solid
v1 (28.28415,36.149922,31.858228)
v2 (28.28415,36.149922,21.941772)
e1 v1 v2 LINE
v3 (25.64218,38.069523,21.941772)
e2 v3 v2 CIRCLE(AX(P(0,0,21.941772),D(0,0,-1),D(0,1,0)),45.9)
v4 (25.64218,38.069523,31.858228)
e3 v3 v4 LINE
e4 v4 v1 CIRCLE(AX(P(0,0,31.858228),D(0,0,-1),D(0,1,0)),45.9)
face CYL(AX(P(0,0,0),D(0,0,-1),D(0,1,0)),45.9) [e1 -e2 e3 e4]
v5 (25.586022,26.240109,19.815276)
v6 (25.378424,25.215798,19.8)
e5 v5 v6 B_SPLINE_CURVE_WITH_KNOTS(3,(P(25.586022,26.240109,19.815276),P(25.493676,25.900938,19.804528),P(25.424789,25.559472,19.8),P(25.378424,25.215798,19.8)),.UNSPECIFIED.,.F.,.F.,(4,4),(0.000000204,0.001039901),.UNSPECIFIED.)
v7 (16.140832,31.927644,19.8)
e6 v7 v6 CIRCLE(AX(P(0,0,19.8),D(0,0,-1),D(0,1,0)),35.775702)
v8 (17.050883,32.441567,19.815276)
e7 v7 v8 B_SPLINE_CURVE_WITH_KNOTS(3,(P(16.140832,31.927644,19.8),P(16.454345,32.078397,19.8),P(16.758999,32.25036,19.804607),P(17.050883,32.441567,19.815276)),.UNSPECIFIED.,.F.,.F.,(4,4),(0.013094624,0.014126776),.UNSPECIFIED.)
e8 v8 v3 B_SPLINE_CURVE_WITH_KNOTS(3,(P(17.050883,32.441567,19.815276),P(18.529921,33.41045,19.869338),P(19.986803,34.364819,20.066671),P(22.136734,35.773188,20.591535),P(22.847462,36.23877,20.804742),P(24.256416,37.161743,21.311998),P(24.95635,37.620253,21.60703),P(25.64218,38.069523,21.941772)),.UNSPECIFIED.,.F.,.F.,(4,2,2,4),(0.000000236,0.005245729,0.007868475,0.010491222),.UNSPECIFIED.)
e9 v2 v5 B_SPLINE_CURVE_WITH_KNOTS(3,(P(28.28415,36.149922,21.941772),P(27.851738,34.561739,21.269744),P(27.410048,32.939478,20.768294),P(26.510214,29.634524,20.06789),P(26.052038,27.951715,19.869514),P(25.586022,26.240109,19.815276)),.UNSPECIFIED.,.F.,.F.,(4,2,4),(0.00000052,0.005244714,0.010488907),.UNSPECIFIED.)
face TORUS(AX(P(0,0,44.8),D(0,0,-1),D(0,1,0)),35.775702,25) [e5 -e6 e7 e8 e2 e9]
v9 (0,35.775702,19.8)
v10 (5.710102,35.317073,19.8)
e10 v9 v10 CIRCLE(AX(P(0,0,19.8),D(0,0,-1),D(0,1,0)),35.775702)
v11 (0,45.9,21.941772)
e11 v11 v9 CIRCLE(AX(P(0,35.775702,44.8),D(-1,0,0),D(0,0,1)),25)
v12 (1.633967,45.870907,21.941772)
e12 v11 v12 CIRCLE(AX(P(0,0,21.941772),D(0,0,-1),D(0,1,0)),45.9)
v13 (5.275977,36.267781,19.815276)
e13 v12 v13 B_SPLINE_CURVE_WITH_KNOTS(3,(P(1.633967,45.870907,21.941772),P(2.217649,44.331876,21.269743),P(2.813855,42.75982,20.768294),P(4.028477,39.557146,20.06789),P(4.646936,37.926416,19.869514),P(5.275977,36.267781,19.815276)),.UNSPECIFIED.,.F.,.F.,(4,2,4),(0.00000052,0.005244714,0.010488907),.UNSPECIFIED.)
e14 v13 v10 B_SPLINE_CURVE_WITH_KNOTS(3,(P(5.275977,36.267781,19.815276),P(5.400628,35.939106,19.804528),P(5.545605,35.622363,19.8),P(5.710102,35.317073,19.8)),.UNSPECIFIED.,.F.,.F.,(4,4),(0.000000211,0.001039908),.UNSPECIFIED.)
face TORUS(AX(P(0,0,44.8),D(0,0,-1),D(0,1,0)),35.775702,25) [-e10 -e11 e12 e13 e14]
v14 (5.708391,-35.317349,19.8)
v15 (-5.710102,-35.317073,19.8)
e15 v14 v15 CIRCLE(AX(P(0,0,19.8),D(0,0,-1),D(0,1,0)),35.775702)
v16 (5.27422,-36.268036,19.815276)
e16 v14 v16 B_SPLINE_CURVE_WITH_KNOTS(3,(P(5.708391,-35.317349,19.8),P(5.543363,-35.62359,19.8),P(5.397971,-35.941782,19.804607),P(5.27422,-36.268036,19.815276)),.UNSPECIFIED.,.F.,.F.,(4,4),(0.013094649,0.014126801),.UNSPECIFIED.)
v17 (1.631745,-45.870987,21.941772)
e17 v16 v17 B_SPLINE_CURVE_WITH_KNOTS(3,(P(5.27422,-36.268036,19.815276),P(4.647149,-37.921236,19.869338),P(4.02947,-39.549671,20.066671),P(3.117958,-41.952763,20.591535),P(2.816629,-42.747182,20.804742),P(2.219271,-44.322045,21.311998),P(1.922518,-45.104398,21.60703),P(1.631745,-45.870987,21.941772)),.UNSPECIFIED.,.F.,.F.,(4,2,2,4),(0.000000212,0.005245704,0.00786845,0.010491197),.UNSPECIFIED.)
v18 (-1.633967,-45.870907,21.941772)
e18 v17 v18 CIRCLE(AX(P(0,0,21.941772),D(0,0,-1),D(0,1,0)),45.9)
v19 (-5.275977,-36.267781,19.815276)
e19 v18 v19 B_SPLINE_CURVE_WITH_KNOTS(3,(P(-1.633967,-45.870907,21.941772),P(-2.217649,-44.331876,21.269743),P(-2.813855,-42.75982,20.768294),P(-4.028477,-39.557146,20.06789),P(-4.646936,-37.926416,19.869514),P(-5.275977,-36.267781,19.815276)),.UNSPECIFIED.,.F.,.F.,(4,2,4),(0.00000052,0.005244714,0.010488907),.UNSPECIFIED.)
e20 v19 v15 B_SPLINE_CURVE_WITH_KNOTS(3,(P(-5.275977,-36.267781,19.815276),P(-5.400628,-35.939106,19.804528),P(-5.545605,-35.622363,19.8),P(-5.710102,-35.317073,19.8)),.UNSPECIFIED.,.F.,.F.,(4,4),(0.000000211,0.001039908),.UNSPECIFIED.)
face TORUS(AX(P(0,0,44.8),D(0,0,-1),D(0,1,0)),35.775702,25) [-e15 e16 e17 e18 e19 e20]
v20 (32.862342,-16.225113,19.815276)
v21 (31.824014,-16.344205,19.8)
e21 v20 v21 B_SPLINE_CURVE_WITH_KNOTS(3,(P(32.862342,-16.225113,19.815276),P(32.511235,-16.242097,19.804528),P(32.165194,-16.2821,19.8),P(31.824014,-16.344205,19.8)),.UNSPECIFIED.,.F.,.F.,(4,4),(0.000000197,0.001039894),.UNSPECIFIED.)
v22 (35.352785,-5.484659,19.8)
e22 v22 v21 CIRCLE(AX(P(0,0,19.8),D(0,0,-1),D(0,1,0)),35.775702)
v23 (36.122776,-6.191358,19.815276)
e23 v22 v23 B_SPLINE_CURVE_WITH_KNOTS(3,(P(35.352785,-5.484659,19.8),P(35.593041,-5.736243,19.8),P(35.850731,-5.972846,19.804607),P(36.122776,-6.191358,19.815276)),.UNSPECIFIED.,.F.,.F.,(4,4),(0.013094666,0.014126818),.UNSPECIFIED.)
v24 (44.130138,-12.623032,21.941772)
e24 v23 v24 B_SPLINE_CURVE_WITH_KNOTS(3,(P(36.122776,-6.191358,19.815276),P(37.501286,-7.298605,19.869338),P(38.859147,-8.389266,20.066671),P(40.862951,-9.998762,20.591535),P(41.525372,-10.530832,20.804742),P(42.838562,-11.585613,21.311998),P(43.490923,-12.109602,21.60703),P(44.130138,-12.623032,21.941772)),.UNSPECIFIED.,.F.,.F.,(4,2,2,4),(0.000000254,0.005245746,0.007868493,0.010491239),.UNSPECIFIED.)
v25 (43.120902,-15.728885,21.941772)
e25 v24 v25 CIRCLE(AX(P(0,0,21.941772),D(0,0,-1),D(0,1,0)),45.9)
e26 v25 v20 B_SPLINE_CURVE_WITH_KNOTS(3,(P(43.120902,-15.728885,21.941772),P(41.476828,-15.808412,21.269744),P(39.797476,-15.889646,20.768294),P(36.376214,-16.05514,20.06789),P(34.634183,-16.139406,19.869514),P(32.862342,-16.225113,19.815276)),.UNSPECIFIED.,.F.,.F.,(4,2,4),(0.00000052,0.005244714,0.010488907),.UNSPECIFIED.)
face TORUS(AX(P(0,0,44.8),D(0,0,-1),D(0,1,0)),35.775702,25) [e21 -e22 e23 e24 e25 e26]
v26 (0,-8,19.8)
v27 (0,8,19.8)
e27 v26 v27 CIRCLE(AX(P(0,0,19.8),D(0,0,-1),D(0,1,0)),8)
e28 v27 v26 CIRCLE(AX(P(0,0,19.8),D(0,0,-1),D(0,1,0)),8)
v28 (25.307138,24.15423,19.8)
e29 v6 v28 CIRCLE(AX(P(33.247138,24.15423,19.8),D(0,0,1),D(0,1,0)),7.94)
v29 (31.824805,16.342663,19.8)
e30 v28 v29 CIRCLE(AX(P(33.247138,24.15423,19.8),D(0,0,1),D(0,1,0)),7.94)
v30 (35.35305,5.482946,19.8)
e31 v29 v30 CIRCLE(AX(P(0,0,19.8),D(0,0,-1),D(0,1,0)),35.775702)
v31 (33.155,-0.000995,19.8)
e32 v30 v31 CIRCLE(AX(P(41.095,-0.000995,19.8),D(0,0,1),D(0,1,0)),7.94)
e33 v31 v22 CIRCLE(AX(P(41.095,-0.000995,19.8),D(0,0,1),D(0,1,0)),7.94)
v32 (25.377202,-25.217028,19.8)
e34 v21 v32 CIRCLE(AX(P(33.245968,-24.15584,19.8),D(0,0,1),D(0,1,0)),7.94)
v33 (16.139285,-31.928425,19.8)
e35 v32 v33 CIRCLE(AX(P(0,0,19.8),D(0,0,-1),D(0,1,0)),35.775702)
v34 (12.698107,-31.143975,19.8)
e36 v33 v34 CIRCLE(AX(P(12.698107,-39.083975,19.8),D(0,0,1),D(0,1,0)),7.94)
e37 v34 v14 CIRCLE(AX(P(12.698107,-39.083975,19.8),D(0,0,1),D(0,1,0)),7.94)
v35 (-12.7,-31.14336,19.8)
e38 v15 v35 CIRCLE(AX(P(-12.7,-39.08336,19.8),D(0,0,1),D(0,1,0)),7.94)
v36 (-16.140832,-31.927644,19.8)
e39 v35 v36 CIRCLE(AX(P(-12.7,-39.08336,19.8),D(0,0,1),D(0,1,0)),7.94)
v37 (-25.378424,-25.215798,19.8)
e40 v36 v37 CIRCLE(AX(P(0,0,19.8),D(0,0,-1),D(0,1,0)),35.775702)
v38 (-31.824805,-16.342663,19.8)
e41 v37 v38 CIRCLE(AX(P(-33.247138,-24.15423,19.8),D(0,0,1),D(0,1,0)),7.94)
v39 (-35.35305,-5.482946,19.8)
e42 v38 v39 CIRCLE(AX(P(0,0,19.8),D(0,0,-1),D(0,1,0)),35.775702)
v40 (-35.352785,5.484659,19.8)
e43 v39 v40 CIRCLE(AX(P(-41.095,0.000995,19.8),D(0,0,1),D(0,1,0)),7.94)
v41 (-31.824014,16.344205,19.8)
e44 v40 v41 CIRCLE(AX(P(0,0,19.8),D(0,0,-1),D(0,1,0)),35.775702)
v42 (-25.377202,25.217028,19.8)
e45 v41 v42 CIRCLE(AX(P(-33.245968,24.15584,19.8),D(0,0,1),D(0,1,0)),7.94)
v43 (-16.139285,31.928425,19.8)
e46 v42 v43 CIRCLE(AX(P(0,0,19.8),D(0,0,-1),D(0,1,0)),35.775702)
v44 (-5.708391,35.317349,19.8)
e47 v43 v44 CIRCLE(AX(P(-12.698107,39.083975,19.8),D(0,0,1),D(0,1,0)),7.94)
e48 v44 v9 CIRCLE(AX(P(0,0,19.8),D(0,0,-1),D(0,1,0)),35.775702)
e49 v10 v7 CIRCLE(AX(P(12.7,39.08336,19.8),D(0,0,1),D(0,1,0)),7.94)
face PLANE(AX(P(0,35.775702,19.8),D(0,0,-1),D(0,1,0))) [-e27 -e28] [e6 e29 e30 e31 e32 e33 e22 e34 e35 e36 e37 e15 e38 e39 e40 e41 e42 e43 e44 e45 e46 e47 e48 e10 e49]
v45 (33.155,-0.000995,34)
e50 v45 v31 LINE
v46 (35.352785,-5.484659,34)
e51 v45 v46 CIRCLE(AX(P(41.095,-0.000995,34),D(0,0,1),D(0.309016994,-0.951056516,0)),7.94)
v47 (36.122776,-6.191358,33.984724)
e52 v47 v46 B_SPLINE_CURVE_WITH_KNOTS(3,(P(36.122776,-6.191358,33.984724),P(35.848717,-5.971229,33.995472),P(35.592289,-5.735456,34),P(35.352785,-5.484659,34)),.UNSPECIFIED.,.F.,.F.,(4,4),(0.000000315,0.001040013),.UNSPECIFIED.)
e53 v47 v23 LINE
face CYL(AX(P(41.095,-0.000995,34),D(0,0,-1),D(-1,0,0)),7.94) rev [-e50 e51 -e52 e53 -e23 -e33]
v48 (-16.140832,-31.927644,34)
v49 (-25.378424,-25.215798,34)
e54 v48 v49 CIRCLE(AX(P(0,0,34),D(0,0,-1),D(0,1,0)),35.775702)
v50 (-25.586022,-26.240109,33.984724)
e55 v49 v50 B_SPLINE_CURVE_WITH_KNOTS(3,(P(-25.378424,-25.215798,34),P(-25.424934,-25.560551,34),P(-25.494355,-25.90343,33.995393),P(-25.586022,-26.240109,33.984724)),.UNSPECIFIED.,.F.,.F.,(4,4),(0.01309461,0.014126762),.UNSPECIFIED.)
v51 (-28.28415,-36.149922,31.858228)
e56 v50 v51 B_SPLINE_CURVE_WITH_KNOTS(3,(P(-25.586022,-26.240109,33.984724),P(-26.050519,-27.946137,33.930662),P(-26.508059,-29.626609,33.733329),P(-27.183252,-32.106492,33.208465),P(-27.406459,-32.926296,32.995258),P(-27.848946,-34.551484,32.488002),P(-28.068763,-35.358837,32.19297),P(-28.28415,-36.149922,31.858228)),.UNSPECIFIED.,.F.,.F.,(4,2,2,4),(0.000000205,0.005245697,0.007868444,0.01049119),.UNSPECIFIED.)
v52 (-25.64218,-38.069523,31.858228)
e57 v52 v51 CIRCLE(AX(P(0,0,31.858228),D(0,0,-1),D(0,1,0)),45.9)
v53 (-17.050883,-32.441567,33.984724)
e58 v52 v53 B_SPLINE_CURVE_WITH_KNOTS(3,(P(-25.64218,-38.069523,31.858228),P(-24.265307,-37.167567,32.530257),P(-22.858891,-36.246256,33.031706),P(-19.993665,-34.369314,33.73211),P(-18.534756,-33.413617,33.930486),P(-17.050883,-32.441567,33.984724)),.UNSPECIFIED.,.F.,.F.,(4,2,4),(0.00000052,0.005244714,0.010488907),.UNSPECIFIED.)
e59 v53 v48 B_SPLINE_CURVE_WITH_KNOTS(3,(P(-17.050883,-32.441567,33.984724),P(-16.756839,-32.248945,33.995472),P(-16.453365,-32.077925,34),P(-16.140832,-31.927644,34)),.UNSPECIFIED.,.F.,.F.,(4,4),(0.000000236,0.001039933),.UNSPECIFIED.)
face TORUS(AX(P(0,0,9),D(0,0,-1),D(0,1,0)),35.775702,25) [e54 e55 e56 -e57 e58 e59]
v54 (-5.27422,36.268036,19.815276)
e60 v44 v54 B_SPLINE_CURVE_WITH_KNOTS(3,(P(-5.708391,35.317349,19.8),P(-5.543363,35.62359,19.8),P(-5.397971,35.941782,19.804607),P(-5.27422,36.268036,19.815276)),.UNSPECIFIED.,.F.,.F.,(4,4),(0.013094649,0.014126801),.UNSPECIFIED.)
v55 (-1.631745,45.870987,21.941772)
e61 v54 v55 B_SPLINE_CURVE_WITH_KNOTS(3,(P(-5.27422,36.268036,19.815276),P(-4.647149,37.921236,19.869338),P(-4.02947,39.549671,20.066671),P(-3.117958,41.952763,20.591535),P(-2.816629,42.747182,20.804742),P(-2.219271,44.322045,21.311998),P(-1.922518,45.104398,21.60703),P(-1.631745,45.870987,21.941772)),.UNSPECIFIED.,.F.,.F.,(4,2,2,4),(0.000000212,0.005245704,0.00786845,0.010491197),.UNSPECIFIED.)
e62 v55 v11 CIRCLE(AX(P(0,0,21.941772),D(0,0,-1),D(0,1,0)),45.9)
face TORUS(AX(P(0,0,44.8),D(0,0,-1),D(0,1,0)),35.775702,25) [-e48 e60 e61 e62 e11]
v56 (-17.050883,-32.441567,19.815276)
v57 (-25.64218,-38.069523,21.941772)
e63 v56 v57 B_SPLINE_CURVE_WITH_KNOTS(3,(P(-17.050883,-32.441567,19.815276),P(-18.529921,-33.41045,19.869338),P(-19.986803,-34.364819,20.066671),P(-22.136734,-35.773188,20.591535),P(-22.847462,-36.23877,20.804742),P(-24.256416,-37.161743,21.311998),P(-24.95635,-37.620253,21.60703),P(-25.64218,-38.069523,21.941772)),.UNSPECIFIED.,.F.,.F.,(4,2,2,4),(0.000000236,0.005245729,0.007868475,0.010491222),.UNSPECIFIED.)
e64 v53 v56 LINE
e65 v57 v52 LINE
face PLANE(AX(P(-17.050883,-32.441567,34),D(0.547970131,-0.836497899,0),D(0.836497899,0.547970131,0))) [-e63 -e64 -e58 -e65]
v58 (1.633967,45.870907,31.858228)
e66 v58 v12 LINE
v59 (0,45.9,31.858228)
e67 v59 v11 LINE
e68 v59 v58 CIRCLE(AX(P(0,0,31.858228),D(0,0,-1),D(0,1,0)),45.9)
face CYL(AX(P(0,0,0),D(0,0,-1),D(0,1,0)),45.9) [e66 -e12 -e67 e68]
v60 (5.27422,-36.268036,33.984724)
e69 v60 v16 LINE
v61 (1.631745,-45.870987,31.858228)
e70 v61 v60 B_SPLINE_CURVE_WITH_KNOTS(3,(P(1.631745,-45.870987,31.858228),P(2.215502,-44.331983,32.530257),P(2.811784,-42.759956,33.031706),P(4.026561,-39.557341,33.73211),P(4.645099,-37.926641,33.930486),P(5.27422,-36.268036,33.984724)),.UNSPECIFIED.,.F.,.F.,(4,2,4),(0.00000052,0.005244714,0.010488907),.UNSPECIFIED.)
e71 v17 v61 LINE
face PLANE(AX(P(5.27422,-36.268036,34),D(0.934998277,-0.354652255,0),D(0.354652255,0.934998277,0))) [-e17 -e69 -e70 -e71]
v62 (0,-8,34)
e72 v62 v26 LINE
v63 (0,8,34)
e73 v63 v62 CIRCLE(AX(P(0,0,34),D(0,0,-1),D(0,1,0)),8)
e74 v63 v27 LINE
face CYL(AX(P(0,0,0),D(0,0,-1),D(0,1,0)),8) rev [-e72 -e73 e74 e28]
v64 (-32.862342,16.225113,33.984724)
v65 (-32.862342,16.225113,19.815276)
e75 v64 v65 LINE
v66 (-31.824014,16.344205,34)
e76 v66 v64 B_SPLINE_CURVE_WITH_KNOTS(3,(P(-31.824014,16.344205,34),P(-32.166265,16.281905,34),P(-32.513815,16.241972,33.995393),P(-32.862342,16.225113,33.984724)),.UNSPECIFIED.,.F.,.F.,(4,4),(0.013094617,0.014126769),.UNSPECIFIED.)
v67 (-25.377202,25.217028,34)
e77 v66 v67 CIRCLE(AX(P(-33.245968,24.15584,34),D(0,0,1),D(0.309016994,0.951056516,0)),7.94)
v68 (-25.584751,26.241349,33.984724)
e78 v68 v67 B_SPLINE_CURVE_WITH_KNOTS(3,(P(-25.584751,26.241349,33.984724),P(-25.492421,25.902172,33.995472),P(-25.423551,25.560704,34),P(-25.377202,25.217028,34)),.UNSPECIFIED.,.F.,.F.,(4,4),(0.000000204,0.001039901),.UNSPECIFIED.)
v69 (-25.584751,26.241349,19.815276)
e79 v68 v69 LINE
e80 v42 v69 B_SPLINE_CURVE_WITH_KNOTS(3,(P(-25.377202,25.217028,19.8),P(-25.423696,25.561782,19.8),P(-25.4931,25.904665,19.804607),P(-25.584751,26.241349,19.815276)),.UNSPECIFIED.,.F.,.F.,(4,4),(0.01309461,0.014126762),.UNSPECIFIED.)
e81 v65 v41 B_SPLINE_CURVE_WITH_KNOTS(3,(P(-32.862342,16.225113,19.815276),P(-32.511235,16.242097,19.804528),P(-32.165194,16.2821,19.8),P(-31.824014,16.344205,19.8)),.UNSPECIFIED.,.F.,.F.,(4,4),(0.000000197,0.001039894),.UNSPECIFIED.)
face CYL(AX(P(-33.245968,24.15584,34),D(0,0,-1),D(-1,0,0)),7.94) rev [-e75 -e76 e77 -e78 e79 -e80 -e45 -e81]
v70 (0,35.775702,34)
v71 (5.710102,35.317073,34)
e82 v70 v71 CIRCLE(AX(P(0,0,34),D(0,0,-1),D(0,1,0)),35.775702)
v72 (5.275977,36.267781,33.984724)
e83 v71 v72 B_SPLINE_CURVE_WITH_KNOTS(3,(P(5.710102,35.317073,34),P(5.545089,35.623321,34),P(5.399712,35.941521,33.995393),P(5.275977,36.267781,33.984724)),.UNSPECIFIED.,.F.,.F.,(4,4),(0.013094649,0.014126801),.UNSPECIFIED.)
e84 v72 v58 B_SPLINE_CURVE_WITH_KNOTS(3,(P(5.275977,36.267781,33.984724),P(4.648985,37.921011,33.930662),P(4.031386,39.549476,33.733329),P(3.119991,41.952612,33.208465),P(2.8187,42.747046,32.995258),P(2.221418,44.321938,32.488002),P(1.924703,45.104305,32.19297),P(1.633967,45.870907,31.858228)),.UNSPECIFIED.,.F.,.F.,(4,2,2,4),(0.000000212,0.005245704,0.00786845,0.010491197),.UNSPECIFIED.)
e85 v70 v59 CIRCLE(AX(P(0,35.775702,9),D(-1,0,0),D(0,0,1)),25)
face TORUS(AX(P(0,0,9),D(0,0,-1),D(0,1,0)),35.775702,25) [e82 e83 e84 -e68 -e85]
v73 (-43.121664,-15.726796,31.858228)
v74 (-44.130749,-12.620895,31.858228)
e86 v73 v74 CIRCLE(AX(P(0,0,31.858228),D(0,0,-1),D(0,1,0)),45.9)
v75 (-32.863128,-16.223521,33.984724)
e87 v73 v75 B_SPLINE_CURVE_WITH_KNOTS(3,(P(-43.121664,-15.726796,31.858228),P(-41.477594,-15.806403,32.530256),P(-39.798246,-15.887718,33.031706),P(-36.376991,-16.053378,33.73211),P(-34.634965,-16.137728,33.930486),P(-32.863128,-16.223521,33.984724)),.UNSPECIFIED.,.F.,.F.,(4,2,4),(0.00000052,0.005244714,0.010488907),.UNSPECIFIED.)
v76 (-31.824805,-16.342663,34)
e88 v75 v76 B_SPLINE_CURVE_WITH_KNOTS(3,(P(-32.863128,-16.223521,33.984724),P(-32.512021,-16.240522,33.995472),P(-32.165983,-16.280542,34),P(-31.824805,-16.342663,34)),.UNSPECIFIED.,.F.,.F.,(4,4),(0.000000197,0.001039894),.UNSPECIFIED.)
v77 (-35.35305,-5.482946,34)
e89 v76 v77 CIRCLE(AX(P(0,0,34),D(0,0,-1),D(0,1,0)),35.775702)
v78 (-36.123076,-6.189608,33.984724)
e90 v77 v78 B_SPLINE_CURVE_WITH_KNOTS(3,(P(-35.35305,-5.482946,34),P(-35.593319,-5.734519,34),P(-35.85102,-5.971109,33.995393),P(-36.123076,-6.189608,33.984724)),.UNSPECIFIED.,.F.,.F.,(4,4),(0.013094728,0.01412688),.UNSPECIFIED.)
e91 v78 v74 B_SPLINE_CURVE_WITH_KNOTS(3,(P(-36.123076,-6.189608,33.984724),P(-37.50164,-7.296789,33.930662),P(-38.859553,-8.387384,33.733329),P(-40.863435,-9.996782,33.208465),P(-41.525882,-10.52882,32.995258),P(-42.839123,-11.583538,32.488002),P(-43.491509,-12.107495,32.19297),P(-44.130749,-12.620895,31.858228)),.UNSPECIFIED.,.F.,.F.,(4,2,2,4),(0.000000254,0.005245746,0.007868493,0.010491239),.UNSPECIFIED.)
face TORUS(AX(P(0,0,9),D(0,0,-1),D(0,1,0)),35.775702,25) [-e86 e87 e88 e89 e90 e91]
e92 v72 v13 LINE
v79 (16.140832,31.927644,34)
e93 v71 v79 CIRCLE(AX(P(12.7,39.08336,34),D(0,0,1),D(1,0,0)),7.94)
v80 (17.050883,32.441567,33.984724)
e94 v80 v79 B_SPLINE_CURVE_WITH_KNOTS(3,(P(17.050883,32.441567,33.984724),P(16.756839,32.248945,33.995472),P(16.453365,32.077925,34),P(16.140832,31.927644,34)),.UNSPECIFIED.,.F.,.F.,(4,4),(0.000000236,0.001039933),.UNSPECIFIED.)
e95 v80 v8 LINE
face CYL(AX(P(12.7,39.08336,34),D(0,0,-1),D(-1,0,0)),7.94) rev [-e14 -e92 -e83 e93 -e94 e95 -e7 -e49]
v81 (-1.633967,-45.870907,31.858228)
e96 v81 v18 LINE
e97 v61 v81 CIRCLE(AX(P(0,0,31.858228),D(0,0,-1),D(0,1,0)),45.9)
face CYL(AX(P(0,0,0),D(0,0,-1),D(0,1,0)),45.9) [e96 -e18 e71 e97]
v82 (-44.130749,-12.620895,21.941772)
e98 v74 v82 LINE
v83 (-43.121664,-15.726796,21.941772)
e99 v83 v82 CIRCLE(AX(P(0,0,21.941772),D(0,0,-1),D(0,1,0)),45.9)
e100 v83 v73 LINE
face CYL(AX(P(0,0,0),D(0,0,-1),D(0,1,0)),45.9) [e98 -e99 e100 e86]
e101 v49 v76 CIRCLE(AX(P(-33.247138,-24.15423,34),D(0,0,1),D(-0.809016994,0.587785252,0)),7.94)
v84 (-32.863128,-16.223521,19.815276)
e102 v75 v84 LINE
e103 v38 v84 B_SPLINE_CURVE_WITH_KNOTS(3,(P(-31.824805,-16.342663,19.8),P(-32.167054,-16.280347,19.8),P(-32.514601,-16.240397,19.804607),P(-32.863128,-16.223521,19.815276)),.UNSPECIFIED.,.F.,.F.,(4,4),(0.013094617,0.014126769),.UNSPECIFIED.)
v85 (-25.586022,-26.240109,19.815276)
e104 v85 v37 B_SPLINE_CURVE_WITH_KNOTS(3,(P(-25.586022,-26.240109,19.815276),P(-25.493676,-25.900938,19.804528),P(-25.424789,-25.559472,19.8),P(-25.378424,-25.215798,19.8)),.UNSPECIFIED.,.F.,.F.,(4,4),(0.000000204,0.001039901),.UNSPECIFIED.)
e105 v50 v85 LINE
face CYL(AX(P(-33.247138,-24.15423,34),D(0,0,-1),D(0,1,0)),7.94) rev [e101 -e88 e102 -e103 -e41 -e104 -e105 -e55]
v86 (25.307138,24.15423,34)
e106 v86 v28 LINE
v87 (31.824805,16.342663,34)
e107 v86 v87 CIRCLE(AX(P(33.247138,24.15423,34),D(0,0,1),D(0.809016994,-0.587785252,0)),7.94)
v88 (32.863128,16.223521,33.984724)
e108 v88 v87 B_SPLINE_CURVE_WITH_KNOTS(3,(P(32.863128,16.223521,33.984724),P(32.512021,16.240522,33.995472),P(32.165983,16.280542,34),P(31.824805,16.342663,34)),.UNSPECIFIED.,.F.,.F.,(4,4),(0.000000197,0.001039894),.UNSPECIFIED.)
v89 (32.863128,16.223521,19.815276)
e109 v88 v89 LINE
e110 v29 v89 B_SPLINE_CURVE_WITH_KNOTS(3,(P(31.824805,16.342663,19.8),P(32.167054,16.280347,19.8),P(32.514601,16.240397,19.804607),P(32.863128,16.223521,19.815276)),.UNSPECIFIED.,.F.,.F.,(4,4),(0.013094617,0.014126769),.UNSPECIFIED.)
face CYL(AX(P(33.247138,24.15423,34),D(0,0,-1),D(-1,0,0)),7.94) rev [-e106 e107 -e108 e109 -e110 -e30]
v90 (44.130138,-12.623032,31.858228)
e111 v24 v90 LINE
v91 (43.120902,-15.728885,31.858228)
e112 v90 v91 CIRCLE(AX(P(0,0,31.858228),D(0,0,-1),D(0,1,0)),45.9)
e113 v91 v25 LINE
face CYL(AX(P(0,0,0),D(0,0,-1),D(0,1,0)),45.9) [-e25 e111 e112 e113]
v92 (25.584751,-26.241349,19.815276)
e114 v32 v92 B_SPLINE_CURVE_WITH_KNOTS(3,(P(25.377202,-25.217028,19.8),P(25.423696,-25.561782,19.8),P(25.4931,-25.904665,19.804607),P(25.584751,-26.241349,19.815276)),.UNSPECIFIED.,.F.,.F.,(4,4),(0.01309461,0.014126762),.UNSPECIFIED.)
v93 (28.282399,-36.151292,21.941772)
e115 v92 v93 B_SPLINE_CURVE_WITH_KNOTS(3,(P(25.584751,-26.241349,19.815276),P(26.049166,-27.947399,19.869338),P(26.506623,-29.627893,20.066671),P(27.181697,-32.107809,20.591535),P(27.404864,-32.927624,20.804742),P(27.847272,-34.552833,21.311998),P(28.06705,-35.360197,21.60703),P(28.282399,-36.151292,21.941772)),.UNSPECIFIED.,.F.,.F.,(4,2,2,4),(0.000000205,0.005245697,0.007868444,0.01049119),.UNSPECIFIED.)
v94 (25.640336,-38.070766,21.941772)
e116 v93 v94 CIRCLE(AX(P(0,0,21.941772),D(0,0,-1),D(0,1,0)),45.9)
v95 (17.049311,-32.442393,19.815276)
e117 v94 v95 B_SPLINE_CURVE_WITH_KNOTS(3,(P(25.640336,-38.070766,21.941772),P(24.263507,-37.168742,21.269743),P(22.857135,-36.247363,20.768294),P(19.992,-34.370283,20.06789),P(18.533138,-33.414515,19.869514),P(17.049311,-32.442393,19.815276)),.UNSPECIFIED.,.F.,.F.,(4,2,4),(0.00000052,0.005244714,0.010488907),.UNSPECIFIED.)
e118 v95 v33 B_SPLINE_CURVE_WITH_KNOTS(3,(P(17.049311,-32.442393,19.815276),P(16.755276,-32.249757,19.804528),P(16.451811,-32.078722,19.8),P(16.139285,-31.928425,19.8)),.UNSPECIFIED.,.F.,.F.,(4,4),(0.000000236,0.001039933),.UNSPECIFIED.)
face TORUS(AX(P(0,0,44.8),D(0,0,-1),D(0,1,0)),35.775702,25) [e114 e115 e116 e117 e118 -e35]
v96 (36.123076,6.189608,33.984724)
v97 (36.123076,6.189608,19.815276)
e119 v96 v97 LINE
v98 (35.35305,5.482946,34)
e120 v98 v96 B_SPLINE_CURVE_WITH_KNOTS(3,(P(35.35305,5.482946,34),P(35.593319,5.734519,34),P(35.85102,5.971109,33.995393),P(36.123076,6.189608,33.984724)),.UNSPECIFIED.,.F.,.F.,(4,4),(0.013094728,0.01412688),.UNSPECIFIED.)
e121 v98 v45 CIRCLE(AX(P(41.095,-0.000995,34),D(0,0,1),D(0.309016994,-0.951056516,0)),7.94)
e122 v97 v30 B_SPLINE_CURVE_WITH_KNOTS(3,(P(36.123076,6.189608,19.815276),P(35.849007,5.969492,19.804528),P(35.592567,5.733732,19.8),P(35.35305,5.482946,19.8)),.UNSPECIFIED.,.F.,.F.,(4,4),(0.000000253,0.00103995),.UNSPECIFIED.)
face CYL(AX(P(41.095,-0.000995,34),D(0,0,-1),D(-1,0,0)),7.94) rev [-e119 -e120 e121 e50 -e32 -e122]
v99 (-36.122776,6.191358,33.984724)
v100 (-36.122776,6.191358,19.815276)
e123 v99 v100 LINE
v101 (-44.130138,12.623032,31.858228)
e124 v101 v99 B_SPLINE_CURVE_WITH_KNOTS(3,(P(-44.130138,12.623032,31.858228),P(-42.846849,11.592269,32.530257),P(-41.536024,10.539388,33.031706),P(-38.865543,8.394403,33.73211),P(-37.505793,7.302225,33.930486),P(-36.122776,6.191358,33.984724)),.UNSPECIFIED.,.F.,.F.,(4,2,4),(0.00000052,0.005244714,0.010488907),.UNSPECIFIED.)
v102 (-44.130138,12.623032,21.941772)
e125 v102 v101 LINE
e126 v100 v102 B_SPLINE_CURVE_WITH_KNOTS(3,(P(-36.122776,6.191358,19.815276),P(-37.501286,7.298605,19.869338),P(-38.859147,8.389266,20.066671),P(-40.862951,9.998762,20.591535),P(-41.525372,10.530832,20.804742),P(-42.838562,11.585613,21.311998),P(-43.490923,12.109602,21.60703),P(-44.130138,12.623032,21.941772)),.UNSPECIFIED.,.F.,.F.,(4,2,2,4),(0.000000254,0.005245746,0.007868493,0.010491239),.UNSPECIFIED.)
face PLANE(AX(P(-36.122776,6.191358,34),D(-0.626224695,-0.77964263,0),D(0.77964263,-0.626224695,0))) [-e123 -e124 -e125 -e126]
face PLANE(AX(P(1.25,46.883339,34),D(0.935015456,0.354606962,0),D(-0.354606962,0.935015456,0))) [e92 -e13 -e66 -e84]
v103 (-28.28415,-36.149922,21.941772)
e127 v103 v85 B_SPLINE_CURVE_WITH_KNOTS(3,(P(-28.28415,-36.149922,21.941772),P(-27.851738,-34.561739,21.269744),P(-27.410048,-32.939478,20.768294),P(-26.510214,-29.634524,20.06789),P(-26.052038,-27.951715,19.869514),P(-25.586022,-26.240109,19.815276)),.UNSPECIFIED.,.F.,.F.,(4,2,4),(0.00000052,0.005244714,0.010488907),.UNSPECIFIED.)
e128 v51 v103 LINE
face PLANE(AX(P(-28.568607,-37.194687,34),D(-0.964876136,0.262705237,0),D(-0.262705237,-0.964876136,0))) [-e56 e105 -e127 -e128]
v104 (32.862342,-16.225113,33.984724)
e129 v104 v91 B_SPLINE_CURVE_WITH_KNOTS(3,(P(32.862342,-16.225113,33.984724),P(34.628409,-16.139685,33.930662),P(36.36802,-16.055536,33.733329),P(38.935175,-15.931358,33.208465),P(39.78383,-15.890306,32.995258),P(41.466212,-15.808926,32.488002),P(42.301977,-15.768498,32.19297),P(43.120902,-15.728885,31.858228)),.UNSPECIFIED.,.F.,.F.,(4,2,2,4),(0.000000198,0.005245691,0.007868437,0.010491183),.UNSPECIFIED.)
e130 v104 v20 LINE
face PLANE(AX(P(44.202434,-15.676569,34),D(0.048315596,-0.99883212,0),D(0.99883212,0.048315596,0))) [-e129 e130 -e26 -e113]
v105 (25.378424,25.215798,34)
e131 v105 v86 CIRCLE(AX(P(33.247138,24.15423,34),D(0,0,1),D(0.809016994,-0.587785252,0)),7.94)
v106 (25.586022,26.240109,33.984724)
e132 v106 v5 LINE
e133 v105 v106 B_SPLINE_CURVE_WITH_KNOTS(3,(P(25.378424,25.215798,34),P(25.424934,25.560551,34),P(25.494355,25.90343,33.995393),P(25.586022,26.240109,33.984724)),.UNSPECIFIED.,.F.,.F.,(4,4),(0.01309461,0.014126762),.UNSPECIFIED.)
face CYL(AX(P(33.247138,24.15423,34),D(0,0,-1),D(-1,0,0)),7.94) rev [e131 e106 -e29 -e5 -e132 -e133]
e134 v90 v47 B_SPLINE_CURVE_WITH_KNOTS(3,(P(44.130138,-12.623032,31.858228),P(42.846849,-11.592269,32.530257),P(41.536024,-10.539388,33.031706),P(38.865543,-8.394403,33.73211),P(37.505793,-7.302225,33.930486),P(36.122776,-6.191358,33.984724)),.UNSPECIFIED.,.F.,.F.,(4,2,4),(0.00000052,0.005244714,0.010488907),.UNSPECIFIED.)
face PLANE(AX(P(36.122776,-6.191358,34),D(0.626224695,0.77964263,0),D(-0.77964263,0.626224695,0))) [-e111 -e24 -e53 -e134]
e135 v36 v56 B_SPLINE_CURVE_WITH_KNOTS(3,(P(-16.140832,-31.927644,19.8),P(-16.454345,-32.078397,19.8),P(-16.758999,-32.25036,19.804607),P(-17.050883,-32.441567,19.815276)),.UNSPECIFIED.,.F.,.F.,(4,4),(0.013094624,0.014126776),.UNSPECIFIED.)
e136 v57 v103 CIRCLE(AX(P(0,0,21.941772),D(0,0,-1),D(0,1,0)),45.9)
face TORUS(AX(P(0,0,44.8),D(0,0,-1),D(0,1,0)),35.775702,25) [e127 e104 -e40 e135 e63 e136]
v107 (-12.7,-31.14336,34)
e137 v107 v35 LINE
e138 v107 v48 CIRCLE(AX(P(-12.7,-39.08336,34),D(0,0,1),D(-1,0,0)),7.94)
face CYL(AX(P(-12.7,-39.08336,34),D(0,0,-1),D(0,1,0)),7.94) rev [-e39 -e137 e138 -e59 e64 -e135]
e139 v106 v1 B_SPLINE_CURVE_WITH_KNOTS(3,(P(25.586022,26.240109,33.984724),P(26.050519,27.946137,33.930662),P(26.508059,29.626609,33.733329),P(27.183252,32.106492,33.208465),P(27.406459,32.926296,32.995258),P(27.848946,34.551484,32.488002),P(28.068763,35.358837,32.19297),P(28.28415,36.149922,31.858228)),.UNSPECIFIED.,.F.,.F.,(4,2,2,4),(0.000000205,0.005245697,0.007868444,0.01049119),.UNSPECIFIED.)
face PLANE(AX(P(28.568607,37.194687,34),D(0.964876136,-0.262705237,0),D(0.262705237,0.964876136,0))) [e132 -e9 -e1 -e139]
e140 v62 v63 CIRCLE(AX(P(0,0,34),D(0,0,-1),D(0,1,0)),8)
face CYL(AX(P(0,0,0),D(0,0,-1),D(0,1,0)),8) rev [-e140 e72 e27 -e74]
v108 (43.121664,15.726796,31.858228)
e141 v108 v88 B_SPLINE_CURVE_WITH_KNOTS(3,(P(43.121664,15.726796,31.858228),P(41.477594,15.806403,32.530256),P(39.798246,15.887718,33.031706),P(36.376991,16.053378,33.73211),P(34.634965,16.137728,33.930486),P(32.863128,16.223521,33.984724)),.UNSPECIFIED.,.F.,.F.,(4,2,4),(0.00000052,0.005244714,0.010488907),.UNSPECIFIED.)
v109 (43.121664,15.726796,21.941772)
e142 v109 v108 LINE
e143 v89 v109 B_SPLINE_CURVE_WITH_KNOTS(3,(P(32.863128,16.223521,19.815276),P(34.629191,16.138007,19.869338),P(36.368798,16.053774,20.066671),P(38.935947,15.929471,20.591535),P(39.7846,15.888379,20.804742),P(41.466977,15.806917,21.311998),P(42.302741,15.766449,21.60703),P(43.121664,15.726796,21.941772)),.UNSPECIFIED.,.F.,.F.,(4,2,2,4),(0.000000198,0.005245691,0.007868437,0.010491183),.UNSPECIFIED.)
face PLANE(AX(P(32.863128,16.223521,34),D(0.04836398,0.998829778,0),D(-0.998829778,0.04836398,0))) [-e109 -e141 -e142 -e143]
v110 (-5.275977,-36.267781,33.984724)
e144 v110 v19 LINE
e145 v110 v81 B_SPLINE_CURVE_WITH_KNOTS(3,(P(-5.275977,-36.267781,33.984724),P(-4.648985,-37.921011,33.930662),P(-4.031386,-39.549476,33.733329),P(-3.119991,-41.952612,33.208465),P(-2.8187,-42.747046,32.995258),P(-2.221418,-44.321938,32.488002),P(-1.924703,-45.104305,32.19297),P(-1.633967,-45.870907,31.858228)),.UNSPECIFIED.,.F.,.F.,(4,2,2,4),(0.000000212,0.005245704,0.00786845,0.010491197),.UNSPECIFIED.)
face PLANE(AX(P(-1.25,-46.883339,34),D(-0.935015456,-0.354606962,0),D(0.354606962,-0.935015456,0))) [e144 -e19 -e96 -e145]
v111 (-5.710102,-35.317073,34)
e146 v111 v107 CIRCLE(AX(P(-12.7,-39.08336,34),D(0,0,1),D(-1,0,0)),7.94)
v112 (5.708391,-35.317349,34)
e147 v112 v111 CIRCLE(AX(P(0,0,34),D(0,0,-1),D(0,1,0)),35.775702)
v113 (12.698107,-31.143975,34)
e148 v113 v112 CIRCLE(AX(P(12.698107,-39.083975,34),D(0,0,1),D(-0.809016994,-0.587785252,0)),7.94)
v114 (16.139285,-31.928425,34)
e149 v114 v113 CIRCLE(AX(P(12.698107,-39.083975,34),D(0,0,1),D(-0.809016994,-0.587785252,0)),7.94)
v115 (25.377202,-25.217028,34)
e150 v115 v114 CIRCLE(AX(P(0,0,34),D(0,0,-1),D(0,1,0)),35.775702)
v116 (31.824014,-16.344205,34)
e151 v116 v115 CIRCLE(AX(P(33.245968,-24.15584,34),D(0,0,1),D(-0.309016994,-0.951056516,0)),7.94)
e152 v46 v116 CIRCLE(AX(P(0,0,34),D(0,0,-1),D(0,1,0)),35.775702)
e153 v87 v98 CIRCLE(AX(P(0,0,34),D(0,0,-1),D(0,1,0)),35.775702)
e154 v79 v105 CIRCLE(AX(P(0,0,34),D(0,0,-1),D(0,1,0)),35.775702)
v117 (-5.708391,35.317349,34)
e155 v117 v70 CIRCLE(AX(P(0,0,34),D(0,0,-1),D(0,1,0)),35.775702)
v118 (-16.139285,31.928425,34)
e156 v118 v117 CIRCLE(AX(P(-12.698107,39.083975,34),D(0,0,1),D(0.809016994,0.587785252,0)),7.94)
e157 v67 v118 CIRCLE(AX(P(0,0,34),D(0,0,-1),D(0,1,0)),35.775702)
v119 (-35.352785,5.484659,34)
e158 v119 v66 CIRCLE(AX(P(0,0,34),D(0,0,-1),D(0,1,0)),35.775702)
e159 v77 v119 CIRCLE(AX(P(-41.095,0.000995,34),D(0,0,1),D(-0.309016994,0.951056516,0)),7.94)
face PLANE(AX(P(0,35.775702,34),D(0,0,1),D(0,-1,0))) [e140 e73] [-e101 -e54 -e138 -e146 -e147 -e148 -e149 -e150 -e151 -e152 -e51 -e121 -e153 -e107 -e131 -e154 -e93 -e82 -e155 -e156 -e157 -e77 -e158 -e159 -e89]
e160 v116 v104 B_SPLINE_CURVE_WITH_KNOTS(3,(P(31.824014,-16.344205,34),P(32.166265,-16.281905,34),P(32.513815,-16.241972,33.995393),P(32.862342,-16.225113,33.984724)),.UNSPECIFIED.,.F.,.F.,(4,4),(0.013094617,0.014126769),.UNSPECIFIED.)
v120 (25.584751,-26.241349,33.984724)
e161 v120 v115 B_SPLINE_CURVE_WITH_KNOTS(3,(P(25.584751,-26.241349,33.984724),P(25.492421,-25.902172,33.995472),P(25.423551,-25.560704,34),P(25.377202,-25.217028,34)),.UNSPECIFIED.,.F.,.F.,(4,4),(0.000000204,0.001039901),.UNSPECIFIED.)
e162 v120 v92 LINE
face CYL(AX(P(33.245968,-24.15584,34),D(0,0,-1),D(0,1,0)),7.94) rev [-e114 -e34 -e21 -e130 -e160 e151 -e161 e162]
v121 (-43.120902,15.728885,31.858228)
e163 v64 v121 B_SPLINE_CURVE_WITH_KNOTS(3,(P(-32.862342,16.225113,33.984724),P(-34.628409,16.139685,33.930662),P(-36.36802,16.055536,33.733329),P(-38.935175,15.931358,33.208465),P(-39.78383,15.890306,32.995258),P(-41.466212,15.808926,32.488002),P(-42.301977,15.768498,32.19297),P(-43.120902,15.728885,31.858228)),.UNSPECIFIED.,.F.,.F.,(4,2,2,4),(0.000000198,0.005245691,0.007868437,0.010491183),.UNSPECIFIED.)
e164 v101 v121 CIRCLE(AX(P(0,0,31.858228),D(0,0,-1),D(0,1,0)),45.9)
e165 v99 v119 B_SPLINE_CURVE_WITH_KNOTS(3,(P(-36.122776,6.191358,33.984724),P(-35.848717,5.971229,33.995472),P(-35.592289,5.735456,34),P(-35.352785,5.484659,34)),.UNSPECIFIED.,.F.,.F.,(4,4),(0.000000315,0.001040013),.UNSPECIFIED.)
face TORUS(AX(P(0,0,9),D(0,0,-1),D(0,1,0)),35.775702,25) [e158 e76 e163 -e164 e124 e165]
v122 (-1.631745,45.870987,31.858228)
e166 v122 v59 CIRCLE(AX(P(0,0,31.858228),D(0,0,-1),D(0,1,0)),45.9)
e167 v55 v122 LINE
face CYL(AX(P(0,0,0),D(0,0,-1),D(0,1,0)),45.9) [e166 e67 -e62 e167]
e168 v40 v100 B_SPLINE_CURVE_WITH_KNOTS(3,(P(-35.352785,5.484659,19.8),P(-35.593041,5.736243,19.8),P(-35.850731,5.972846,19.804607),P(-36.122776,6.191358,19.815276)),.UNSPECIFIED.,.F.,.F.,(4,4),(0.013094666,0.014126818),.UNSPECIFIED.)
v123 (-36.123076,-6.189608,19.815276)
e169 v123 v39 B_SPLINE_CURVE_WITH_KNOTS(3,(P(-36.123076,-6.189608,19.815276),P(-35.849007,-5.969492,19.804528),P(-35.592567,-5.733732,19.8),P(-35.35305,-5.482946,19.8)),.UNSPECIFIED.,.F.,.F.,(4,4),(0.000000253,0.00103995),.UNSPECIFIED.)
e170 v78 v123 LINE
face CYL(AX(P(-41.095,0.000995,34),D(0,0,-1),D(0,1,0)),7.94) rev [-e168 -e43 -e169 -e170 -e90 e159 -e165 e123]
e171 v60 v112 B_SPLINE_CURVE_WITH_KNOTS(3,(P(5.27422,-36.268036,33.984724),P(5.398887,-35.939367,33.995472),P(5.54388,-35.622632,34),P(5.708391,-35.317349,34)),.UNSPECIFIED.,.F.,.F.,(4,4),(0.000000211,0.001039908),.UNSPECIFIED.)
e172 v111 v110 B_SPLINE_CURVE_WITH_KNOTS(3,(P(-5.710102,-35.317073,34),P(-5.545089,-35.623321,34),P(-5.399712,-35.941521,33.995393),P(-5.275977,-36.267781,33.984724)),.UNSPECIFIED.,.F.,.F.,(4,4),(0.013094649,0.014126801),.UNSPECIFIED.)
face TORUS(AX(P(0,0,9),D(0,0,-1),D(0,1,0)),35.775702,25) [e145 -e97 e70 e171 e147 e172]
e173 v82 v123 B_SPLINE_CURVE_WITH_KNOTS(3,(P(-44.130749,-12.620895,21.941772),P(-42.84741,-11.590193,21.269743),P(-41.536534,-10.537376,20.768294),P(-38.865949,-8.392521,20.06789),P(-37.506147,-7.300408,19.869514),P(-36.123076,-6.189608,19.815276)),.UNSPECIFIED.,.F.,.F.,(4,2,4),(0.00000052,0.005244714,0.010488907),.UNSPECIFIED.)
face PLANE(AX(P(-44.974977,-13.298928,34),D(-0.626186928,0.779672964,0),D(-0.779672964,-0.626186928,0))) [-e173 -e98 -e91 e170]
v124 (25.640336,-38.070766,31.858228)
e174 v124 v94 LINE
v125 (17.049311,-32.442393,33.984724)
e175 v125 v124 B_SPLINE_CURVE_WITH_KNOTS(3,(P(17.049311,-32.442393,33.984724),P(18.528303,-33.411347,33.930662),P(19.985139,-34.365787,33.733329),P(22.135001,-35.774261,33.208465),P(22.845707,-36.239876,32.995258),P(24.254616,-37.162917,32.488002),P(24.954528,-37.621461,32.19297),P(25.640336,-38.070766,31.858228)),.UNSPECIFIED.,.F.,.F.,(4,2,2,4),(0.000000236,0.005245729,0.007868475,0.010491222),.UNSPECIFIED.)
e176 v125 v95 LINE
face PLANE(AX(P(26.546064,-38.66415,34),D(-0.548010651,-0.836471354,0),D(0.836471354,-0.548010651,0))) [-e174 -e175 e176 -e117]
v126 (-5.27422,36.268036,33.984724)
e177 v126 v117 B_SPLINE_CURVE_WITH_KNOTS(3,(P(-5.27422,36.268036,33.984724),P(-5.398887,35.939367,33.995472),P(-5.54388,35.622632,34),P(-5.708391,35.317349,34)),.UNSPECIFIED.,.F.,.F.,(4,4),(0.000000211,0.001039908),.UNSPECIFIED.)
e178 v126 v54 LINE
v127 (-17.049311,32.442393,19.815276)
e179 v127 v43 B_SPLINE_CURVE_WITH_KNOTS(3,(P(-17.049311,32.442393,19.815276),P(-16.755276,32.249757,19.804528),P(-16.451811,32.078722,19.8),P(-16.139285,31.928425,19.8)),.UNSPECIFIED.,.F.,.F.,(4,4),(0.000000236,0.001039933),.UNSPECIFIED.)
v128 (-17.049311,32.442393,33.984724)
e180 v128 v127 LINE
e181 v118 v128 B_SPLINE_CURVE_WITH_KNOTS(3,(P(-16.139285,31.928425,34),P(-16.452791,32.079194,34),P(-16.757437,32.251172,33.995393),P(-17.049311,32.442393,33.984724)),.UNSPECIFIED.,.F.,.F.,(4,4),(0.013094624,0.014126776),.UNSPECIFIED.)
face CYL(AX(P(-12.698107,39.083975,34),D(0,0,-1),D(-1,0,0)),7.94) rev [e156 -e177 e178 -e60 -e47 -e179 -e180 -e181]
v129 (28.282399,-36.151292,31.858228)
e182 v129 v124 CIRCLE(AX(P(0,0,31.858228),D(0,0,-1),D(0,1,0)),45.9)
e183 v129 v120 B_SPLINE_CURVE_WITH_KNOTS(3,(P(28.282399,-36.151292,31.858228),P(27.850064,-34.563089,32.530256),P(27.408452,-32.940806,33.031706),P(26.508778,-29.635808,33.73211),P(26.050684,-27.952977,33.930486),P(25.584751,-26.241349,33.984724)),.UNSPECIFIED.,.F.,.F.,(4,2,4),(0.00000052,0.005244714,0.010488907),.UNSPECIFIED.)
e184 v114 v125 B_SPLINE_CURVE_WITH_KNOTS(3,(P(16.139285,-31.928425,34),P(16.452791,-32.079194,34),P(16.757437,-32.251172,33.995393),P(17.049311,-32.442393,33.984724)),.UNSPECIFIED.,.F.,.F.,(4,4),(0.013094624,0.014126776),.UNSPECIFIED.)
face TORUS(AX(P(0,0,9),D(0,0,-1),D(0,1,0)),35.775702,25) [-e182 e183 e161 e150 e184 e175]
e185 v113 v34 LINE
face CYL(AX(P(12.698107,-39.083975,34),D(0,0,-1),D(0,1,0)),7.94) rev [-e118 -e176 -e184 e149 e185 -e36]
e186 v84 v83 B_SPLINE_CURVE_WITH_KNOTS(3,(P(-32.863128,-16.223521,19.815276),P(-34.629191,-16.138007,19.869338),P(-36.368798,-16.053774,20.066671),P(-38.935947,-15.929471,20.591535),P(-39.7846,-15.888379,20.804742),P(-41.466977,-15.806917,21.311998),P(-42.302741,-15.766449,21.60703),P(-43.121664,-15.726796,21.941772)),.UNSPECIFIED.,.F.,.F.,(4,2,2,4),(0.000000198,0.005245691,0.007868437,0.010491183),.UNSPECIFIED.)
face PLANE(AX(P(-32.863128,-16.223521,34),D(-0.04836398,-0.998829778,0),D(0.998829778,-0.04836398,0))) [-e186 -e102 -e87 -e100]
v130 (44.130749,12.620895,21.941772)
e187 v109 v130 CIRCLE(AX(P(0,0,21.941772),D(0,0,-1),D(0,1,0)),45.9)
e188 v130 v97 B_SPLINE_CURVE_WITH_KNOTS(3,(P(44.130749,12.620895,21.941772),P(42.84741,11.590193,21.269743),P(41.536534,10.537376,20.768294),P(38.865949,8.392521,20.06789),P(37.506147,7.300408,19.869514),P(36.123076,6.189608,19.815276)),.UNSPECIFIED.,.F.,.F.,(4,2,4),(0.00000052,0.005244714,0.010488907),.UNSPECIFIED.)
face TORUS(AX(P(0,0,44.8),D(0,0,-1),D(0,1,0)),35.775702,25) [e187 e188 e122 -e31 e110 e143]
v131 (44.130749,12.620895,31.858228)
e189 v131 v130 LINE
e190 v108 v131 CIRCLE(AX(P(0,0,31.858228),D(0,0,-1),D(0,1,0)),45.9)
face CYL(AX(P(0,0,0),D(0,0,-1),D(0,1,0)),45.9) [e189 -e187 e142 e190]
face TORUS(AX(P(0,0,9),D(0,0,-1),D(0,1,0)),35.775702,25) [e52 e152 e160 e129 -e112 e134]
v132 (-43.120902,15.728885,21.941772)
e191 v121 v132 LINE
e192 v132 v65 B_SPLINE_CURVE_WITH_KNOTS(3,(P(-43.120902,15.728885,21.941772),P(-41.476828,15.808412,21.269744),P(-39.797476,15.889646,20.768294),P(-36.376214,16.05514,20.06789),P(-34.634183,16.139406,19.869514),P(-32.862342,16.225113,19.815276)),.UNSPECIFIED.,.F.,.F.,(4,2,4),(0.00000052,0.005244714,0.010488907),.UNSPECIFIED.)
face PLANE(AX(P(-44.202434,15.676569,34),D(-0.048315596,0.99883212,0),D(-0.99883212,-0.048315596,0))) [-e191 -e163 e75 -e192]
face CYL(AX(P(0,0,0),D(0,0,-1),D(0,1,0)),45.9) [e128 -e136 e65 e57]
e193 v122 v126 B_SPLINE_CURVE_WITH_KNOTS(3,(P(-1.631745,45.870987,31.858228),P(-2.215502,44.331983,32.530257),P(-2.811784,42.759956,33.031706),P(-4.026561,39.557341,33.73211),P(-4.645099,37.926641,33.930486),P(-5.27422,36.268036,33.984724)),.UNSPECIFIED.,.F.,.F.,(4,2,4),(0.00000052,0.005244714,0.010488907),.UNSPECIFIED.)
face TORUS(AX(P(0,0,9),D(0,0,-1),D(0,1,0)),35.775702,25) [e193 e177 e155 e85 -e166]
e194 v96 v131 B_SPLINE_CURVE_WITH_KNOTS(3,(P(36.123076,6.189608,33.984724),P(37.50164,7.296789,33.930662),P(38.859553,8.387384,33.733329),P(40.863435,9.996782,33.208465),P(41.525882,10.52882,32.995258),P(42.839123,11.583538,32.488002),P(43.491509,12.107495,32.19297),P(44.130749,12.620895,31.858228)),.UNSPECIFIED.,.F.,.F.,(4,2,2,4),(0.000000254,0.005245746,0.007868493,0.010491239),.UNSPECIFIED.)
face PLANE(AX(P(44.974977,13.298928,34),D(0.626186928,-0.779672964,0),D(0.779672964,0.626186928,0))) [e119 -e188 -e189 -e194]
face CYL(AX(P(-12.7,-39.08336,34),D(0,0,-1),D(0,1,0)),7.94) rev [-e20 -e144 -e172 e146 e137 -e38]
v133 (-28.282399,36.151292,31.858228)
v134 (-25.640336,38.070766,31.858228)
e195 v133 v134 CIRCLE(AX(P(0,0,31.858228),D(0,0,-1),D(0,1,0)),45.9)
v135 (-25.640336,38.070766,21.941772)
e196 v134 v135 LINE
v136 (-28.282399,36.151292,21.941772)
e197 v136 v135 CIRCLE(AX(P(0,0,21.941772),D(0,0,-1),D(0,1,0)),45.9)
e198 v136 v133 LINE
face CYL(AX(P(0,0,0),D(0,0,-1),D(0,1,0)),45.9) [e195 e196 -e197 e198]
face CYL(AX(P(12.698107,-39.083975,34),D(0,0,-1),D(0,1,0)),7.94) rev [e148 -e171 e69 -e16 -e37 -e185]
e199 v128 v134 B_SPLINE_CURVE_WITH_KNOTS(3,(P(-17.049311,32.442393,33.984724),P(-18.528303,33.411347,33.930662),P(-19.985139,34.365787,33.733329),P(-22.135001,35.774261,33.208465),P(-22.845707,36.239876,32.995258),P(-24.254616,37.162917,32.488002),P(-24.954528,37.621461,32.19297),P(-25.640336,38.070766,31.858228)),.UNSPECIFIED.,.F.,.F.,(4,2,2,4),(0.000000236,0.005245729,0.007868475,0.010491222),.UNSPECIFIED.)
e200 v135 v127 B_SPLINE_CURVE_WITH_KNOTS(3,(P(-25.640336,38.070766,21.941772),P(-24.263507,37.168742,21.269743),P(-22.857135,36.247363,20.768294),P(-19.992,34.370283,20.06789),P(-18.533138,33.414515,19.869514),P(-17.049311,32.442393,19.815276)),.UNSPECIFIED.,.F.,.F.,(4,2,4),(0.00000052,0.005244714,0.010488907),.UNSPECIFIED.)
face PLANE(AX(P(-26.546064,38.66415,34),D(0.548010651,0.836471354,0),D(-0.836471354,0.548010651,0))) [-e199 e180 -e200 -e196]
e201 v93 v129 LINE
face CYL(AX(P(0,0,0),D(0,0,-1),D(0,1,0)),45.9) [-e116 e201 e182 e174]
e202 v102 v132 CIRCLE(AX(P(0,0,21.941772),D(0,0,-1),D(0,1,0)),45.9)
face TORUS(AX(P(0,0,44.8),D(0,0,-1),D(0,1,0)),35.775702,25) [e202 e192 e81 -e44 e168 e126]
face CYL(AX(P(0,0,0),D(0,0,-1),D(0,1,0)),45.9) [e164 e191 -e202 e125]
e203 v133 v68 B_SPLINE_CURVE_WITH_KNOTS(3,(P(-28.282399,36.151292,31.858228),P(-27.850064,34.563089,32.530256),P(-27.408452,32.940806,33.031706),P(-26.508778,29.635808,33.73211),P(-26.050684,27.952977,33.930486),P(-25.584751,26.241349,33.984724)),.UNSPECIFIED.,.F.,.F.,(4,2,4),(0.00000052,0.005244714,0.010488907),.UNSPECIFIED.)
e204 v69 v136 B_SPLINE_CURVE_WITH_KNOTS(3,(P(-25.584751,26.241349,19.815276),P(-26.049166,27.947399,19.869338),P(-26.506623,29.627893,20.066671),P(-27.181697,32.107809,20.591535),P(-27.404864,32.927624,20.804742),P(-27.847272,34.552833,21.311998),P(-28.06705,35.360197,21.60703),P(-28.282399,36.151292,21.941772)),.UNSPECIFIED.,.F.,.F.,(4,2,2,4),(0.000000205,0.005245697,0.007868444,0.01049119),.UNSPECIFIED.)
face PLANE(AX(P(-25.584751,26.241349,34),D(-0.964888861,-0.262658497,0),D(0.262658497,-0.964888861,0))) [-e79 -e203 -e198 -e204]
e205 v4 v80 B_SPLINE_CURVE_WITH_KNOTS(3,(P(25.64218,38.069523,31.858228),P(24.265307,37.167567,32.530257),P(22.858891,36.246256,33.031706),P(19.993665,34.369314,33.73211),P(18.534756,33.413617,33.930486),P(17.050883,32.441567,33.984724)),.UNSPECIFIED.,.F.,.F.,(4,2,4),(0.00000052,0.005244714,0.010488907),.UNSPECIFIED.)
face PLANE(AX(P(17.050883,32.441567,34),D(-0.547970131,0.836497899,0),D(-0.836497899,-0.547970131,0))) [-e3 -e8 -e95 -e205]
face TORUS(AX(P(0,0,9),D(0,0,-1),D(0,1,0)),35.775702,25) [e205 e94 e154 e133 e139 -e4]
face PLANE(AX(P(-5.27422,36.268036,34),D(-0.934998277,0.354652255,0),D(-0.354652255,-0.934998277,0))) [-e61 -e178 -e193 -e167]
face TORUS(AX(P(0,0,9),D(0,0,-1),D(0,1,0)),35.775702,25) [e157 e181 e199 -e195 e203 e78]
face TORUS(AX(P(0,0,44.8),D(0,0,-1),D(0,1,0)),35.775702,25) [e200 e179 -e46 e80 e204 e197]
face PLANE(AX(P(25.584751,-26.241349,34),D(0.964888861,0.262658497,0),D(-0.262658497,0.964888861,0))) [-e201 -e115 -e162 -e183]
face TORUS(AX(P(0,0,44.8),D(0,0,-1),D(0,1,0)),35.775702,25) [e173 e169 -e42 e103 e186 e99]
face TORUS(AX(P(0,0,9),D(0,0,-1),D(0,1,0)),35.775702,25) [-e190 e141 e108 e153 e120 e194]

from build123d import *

# Parameters (mm, degrees)
CUT_EXTRUDE_1_DEPTH      = 74.277691012
PATTERN_CIRCULAR_1_COUNT = 10


with BuildPart() as part:
    # 草图4 → 旋转1 (revolve)
    with BuildSketch(Plane(origin=(0, 0, 0), x_dir=(0, 0, -1), z_dir=(1, 0, 0))):
        with BuildLine():
            Line((-19.8, 35.775702269), (-19.8, 8))
            Line((-19.8, 8), (-34, 8))
            Line((-34, 8), (-34, 35.775702269))
            ThreePointArc((-34, 35.775702269), (-33.458696863, 40.949883148), (-31.858228179, 45.9))
            Line((-31.858228179, 45.9), (-21.941771821, 45.9))
            ThreePointArc((-21.941771821, 45.9), (-20.341303137, 40.949883148), (-19.8, 35.775702269))
        make_face()
    revolve(axis=Axis((0, 0, 0), (0, 0, 1)))

    # 草图5 → 切除-拉伸1 (cut, through all)
    with BuildSketch(Plane.XY):
        with BuildLine():
            Line((1.25, 46.883339258), (5.275977282, 36.26778067))
            ThreePointArc((5.275977282, 36.26778067), (10.246222168, 31.53203064), (17.05088284, 32.44156663))
            Line((17.05088284, 32.44156663), (26.547937038, 38.662863823))
            ThreePointArc((26.547937038, 38.662863823), (14.49397737, 44.604199578), (1.25, 46.883339258))
        make_face()
    cut_extrude_1 = extrude(amount=CUT_EXTRUDE_1_DEPTH, mode=Mode.SUBTRACT)

    # 阵列(圆周)1: 切除-拉伸1 ×10 about axis
    pattern_circular_1_axis = Axis((0, 0, 0), (0, 0, 1))
    for i in range(1, PATTERN_CIRCULAR_1_COUNT):
        add(cut_extrude_1.rotate(pattern_circular_1_axis, i * 360 / PATTERN_CIRCULAR_1_COUNT), mode=Mode.SUBTRACT)


solid = part.part
